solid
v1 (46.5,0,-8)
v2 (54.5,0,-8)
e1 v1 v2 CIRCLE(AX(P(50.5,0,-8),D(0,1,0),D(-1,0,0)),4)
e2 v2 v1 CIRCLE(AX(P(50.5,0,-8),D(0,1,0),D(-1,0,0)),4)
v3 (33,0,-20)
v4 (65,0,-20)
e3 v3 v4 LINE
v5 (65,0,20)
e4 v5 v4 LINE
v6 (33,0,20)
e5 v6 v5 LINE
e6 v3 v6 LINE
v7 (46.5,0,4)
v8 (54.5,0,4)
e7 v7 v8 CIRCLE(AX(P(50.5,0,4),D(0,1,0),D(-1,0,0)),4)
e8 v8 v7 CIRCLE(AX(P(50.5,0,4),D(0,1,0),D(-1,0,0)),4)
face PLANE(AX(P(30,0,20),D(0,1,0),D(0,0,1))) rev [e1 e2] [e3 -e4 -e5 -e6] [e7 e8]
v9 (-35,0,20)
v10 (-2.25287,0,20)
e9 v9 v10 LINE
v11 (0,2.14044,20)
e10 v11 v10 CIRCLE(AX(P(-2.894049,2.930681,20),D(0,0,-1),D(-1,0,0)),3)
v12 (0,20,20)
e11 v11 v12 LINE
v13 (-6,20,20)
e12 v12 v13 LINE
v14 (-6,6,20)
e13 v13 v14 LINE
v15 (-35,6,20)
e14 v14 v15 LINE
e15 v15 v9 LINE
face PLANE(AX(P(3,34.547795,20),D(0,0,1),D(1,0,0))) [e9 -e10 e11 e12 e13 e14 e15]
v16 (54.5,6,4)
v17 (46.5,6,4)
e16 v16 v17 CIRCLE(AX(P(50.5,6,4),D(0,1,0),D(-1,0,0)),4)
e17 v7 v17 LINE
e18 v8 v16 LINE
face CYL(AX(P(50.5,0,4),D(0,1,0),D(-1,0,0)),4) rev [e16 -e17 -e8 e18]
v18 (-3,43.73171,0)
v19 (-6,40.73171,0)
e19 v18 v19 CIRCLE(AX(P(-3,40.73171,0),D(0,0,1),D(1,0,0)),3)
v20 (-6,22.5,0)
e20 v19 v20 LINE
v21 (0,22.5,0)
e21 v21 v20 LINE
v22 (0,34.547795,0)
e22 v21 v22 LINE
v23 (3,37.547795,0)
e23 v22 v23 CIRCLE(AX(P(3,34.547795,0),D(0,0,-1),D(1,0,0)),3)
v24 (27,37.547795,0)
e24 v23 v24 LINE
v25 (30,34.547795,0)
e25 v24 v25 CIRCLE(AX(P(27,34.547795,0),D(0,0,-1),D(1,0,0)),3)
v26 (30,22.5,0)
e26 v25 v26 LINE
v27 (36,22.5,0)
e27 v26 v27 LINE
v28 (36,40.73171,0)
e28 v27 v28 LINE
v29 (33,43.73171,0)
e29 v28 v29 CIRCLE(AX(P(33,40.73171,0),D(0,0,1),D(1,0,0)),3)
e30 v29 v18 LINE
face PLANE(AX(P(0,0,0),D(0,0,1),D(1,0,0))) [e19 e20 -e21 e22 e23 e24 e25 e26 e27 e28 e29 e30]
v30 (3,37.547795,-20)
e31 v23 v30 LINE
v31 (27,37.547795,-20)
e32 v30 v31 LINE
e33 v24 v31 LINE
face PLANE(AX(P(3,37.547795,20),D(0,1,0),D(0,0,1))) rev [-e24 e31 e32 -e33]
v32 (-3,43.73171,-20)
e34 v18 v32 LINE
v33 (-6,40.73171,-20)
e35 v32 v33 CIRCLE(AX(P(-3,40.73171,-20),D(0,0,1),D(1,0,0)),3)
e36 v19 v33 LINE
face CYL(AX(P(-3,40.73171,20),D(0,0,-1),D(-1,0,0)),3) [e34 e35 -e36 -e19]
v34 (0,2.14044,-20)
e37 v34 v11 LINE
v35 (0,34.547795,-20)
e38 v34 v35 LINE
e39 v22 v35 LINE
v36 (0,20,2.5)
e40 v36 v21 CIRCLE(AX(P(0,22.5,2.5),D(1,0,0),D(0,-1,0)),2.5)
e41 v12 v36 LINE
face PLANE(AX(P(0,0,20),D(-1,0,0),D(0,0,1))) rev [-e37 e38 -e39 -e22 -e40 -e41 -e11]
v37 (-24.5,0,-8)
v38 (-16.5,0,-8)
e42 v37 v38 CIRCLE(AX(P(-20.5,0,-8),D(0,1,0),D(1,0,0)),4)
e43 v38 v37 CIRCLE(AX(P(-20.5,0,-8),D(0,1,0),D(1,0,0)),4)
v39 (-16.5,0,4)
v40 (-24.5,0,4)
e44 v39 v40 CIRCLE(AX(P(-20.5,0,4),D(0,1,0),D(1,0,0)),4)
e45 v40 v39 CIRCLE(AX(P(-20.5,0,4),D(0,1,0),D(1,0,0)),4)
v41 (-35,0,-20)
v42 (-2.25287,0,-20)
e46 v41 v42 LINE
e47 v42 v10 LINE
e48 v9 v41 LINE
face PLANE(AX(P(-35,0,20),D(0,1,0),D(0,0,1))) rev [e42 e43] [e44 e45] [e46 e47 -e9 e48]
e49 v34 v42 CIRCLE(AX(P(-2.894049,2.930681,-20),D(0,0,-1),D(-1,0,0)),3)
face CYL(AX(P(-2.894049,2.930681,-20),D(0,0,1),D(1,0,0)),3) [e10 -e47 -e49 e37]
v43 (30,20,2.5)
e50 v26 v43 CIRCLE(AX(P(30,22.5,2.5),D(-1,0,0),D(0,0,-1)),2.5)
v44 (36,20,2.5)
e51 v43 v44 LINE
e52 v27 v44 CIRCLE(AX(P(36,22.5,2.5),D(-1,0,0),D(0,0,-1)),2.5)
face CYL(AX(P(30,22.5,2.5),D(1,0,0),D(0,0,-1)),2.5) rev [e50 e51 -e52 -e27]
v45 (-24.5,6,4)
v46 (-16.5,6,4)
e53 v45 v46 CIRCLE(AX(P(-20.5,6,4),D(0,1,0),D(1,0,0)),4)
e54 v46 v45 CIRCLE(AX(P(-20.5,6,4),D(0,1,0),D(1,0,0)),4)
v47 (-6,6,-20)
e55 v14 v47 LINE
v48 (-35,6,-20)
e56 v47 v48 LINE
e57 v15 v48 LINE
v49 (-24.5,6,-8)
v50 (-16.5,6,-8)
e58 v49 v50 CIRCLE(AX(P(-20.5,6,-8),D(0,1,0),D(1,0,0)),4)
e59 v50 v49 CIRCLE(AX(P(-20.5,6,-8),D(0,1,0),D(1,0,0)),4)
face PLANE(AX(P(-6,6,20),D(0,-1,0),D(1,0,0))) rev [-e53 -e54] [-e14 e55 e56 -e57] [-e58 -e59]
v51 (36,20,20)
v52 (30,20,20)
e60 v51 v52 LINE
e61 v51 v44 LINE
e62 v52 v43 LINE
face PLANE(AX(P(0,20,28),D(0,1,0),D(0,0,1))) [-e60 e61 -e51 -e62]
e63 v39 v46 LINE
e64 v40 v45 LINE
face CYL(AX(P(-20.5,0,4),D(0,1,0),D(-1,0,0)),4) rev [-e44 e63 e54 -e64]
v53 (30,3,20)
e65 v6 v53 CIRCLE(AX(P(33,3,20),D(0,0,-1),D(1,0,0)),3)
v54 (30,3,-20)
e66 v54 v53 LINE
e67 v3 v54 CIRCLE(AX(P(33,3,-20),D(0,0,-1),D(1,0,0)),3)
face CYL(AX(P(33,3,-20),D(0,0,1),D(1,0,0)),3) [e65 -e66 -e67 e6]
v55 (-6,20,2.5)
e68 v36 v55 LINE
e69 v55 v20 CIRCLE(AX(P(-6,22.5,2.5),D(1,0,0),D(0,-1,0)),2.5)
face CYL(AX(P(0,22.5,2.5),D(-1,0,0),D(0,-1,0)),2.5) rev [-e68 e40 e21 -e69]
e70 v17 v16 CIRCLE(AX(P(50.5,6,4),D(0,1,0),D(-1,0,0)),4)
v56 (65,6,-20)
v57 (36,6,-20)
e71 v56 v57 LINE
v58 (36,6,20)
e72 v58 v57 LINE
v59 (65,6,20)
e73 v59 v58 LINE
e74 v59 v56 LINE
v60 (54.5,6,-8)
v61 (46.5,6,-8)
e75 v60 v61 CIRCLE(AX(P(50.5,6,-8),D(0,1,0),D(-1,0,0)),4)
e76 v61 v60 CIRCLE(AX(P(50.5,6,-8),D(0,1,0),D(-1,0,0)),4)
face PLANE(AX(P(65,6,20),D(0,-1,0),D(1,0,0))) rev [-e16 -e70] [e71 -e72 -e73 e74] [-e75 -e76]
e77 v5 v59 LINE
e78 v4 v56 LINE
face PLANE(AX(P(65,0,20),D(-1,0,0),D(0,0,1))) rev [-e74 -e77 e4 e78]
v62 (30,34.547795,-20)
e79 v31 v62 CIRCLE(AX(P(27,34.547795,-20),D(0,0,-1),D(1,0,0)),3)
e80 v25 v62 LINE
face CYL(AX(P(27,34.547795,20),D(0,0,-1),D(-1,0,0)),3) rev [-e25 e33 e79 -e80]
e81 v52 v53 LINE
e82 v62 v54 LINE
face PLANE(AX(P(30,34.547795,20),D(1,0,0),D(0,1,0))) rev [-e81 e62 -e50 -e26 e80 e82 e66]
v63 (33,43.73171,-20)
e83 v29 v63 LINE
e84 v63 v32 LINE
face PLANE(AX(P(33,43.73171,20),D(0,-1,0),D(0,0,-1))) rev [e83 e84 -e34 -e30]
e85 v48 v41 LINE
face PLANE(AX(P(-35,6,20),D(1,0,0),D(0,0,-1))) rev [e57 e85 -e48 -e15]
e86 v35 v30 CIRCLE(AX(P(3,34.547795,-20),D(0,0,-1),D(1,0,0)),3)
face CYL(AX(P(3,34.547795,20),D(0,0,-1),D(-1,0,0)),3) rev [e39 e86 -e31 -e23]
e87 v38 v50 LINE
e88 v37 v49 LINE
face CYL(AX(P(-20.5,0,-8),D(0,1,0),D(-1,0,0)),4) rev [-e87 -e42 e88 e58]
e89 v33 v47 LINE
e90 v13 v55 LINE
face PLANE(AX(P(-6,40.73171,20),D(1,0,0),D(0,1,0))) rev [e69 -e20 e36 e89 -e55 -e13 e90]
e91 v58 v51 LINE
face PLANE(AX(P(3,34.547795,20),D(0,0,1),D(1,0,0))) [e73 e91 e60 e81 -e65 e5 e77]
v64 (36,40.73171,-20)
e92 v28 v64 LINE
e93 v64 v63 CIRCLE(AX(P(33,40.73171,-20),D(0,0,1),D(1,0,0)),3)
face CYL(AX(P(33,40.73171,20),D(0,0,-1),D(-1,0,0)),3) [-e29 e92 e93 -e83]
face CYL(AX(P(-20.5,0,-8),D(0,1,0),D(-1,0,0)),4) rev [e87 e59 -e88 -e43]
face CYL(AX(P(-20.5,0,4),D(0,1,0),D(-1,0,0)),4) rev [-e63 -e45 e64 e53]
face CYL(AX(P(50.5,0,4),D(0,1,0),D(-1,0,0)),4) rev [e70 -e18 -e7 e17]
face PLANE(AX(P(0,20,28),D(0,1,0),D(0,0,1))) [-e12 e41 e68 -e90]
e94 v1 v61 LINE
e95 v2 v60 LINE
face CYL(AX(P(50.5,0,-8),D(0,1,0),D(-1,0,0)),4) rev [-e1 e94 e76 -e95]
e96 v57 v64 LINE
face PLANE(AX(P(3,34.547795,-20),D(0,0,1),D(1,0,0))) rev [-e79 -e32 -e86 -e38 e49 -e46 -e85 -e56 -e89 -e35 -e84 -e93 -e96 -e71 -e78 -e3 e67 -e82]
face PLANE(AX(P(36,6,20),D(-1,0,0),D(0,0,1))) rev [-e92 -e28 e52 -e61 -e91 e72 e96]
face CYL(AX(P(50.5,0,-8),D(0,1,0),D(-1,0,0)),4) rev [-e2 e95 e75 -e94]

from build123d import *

# Parameters (mm, degrees)
BRACKET_BODY_40MM_DEPTH          = 20
STEPPED_START                    = 28
STEPPED_RELIEF_CUT_28MM_DEPTH    = 28
CORNER_ROUND_CUT_A_R3_DEPTH      = 88.96284726
CORNER_ROUND_CUT_B_R3_DEPTH      = 81.854576235
CORNER_ROUND_CUT_B_R3_DEPTH_BACK = 81.854576235
CORNER_FILL_BOSS_A_6MM_DEPTH     = 6
CORNER_START                     = -6
CORNER_FILL_BOSS_B_6MM_DEPTH     = 6
MOUNTING_HOLES_SKETCH_R          = 4
FLANGE_MOUNTING_HOLES_DEPTH      = 78.77327287


with BuildPart() as part:
    # Bracket Profile Sketch → Bracket Body 40mm (new, symmetric)
    with BuildSketch(Plane.XY):
        with BuildLine():
            Line((30, 0), (65, 0))
            Line((65, 0), (65, 6))
            Line((65, 6), (36, 6))
            Line((36, 6), (36, 40.731710442))
            ThreePointArc((36, 40.731710442), (35.121320344, 42.853030785), (33, 43.731710442))
            Line((33, 43.731710442), (-3, 43.731710442))
            ThreePointArc((-3, 43.731710442), (-5.121320344, 42.853030785), (-6, 40.731710442))
            Line((-6, 40.731710442), (-6, 6))
            Line((-6, 6), (-35, 6))
            Line((-35, 6), (-35, 0))
            Line((-35, 0), (0, 0))
            Line((0, 0), (0, 34.547795072))
            ThreePointArc((0, 34.547795072), (0.878679656, 36.669115416), (3, 37.547795072))
            Line((3, 37.547795072), (27, 37.547795072))
            ThreePointArc((27, 37.547795072), (29.121320344, 36.669115416), (30, 34.547795072))
            Line((30, 34.547795072), (30, 0))
        make_face()
    extrude(amount=BRACKET_BODY_40MM_DEPTH, both=True)

    # Relief Cut Sketch → Stepped Relief Cut 28mm (cut)
    with BuildSketch(Plane.XY.offset(STEPPED_START)):
        with BuildLine():
            Line((33, 43.731710442), (-3, 43.731710442))
            ThreePointArc((-3, 43.731710442), (-5.121320344, 42.853030785), (-6, 40.731710442))
            Line((-6, 40.731710442), (-6, 20))
            Line((-6, 20), (0, 20))
            Line((0, 20), (0, 34.547795072))
            ThreePointArc((0, 34.547795072), (0.878679656, 36.669115416), (3, 37.547795072))
            Line((3, 37.547795072), (27, 37.547795072))
            ThreePointArc((27, 37.547795072), (29.121320344, 36.669115416), (30, 34.547795072))
            Line((30, 34.547795072), (30, 20))
            Line((30, 20), (36, 20))
            Line((36, 20), (36, 40.731710442))
            ThreePointArc((36, 40.731710442), (35.121320344, 42.853030785), (33, 43.731710442))
        make_face()
    extrude(amount=-STEPPED_RELIEF_CUT_28MM_DEPTH, mode=Mode.SUBTRACT)

    # Corner Round Cut A Sketch → Corner Round Cut A R3 (cut, through all)
    with BuildSketch(Plane.XY.offset(20)):
        with BuildLine():
            Line((0, 2.140440117), (0, 0))
            Line((0, 0), (-2.252870035, 0))
            ThreePointArc((-2.252870035, 0), (-0.827692267, 0.755785384), (0, 2.140440117))
        make_face()
    extrude(amount=-CORNER_ROUND_CUT_A_R3_DEPTH, mode=Mode.SUBTRACT)

    # Corner Round Cut B Sketch → Corner Round Cut B R3 (cut, two sides: drawn at the far end of the back side and taken through both)
    with BuildSketch(Plane.XY.offset(-CORNER_ROUND_CUT_B_R3_DEPTH_BACK)):
        with BuildLine():
            Line((30, 0), (30, 3))
            ThreePointArc((30, 3), (30.878679656, 0.878679656), (33, 0))
            Line((33, 0), (30, 0))
        make_face()
    extrude(amount=CORNER_ROUND_CUT_B_R3_DEPTH + CORNER_ROUND_CUT_B_R3_DEPTH_BACK, mode=Mode.SUBTRACT)

    # Corner Fill Boss A Sketch → Corner Fill Boss A 6mm (add)
    with BuildSketch(Plane.ZY.offset(6)):
        with BuildLine():
            Line((0, 20), (0, 22.5))
            ThreePointArc((0, 22.5), (0.732233047, 20.732233047), (2.5, 20))
            Line((2.5, 20), (0, 20))
        make_face()
    extrude(amount=-CORNER_FILL_BOSS_A_6MM_DEPTH)

    # Corner Fill Boss B Sketch → Corner Fill Boss B 6mm (add)
    with BuildSketch(Plane(origin=(36, 0, 0), x_dir=(0, 0, -1), z_dir=(1, 0, 0)).offset(CORNER_START)):
        with BuildLine():
            Line((0, 22.5), (0, 20))
            Line((0, 20), (-2.5, 20))
            ThreePointArc((-2.5, 20), (-0.732233047, 20.732233047), (0, 22.5))
        make_face()
    extrude(amount=CORNER_FILL_BOSS_B_6MM_DEPTH)

    # Mounting Holes Sketch → Flange Mounting Holes (cut, through all)
    with BuildSketch(Plane(origin=(0, 6, 0), x_dir=(1, 0, 0), z_dir=(0, 1, 0))):
        with Locations(Location((50.5, -4, 0), (0, 0, 180))):
            Circle(MOUNTING_HOLES_SKETCH_R)
        with Locations(Location((50.5, 8, 0), (0, 0, 180))):
            Circle(MOUNTING_HOLES_SKETCH_R)
        with Locations((-20.5, -4)):
            Circle(MOUNTING_HOLES_SKETCH_R)
        with Locations((-20.5, 8)):
            Circle(MOUNTING_HOLES_SKETCH_R)
    extrude(amount=-FLANGE_MOUNTING_HOLES_DEPTH, mode=Mode.SUBTRACT)


solid = part.part
